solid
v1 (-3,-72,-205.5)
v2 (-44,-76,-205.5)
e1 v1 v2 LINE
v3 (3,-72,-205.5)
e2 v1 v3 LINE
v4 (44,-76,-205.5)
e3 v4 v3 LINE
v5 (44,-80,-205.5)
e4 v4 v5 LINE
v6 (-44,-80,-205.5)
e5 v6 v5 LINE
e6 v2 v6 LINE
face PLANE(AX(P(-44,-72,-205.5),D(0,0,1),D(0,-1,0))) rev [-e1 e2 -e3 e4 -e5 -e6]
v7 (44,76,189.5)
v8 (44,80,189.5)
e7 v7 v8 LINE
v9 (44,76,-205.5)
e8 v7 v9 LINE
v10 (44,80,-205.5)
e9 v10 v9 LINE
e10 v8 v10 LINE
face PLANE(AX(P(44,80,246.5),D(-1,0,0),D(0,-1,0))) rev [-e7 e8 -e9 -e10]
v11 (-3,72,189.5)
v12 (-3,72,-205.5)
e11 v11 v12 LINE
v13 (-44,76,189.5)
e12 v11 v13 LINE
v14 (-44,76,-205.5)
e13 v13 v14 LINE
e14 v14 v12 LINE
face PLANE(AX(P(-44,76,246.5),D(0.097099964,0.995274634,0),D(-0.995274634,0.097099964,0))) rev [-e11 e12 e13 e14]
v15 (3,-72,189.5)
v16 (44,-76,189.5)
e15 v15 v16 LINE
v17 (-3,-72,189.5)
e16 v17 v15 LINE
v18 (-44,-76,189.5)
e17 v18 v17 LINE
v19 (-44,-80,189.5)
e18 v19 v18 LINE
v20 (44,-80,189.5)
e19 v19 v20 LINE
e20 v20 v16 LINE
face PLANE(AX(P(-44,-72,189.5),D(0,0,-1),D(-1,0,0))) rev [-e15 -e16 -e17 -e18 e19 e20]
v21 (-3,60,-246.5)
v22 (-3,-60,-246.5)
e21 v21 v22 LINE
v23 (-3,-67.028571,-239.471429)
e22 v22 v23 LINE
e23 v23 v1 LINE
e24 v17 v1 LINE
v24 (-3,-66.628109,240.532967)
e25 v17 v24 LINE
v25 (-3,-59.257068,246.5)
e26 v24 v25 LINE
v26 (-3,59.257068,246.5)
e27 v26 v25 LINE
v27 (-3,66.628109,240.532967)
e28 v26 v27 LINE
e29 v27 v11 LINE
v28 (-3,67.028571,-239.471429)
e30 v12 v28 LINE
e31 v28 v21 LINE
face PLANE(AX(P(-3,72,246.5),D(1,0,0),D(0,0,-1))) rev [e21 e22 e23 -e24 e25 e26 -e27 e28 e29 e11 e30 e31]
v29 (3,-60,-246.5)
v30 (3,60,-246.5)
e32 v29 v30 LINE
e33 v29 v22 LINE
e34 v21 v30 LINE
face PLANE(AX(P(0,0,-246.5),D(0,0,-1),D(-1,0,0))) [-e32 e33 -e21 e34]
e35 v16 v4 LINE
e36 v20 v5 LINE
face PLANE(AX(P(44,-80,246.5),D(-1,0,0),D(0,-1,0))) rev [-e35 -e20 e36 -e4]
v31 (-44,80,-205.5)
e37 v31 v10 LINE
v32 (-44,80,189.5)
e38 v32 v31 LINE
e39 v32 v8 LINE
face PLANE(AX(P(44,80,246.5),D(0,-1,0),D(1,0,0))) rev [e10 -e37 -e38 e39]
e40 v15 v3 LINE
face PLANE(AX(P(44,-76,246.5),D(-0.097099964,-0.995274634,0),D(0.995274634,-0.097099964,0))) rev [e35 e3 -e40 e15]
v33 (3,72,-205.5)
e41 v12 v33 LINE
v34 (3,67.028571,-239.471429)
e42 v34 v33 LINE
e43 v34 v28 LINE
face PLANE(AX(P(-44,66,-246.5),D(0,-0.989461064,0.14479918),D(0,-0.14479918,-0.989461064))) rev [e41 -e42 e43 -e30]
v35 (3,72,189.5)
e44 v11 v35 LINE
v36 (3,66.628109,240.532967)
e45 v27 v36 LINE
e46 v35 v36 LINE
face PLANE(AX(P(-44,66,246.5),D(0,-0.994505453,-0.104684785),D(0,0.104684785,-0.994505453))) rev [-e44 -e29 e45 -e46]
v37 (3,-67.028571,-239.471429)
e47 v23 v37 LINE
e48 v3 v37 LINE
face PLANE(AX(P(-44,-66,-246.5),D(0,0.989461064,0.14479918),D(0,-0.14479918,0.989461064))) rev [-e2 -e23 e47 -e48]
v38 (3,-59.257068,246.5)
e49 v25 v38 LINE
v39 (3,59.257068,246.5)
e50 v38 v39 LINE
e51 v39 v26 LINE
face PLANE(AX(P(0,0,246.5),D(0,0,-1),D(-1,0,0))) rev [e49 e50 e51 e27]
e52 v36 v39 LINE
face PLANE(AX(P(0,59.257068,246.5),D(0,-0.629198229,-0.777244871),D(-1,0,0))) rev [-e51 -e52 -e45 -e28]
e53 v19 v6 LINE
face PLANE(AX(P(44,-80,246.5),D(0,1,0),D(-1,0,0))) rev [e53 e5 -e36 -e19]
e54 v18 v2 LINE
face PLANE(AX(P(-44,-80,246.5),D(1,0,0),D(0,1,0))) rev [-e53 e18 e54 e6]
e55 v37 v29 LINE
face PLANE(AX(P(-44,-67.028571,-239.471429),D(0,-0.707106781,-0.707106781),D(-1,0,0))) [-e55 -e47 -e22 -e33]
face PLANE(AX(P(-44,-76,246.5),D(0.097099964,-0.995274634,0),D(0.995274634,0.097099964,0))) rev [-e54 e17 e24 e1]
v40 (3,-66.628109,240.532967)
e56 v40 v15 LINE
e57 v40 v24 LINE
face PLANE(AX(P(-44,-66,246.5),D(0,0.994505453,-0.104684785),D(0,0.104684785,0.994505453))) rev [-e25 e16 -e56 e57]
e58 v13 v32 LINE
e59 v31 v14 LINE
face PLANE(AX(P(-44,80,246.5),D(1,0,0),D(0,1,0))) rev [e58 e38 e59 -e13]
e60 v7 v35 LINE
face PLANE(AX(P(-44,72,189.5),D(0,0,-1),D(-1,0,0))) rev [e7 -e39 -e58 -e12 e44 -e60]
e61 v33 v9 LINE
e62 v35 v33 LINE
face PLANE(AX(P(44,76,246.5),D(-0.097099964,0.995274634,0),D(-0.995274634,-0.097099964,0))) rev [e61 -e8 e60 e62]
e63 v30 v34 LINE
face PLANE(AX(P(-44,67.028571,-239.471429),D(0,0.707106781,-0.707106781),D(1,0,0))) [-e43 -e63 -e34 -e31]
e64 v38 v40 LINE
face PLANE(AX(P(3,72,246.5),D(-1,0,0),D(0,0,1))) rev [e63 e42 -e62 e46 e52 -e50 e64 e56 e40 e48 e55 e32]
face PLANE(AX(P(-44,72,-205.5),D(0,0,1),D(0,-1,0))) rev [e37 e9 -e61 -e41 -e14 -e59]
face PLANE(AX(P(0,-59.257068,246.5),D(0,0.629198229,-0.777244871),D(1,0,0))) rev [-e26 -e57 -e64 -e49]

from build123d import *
from OCP.BRepFilletAPI import BRepFilletAPI_MakeChamfer

# Parameters (mm, degrees)
EXTRUDE_1_DEPTH          = 246.5
CUT_EXTRUDE_1_DEPTH      = 263.865459884
CUT_EXTRUDE_1_DEPTH_BACK = 263.865459884
CHAMFER_1_SIZE           = 6
CHAMFER_1_SIZE2          = 7.103434065
CHAMFER_1_SIZE2_2        = 6.742931709


with BuildPart() as part:
    # 草图1 → 凸台-拉伸1 (new, symmetric)
    with BuildSketch(Plane.XY):
        Polygon((44, 80), (-44, 80), (-44, 76), (-3, 72), (-3, -72), (-44, -76), (-44, -80), (44, -80), (44, -76), (3, -72), (3, 72), (44, 76), align=None)
    extrude(amount=EXTRUDE_1_DEPTH, both=True)

    # 草图3 → 切除-拉伸1 (cut, two sides: drawn at the far end of the back side and taken through both)
    with BuildSketch(Plane(origin=(0, 0, 0), x_dir=(0, 0, -1), z_dir=(1, 0, 0)).offset(-CUT_EXTRUDE_1_DEPTH_BACK)):
        Polygon((-246.5, 66), (-189.5, 72), (-189.5, 80), (-246.5, 80), align=None)
        Polygon((246.5, 80), (246.5, 66), (205.5, 72), (205.5, 80), align=None)
        Polygon((246.5, -66), (205.5, -72), (205.5, -80), (246.5, -80), align=None)
        Polygon((-246.5, -80), (-246.5, -66), (-189.5, -72), (-189.5, -80), align=None)
    extrude(amount=CUT_EXTRUDE_1_DEPTH + CUT_EXTRUDE_1_DEPTH_BACK, mode=Mode.SUBTRACT)

    # 倒角1: one chamfer whose edges measure the first distance from different faces: ONE call of the kernel's chamfer builder (chamfer() names one face for all edges)
    chamfer_1_edges_1 = [part.edges().sort_by_distance(p)[0] for p in [
        (0, 66, -246.5),
        (0, -66, -246.5),
    ]]
    chamfer_1_side_1 = [part.faces().sort_by_distance(p)[0] for p in [
        (0, 0, -246.5),
    ]]
    chamfer_1_edges_2 = [part.edges().sort_by_distance(p)[0] for p in [
        (0, 66, 246.5),
    ]]
    chamfer_1_side_2 = [part.faces().sort_by_distance(p)[0] for p in [
        (0, 69, 218),
    ]]
    chamfer_1_edges_3 = [part.edges().sort_by_distance(p)[0] for p in [
        (0, -66, 246.5),
    ]]
    chamfer_1_side_3 = [part.faces().sort_by_distance(p)[0] for p in [
        (0, -69, 218),
    ]]
    chamfer_1 = BRepFilletAPI_MakeChamfer(part.part.solid().wrapped)
    for e in chamfer_1_edges_1:
        chamfer_1.Add(CHAMFER_1_SIZE, CHAMFER_1_SIZE2, e.wrapped, chamfer_1_side_1[0].wrapped)  # the first distance lies on this face
    for e in chamfer_1_edges_2:
        chamfer_1.Add(CHAMFER_1_SIZE, CHAMFER_1_SIZE2_2, e.wrapped, chamfer_1_side_2[0].wrapped)  # the first distance lies on this face
    for e in chamfer_1_edges_3:
        chamfer_1.Add(CHAMFER_1_SIZE, CHAMFER_1_SIZE2_2, e.wrapped, chamfer_1_side_3[0].wrapped)  # the first distance lies on this face
    add(Compound.cast(chamfer_1.Shape()), mode=Mode.REPLACE)


solid = part.part
